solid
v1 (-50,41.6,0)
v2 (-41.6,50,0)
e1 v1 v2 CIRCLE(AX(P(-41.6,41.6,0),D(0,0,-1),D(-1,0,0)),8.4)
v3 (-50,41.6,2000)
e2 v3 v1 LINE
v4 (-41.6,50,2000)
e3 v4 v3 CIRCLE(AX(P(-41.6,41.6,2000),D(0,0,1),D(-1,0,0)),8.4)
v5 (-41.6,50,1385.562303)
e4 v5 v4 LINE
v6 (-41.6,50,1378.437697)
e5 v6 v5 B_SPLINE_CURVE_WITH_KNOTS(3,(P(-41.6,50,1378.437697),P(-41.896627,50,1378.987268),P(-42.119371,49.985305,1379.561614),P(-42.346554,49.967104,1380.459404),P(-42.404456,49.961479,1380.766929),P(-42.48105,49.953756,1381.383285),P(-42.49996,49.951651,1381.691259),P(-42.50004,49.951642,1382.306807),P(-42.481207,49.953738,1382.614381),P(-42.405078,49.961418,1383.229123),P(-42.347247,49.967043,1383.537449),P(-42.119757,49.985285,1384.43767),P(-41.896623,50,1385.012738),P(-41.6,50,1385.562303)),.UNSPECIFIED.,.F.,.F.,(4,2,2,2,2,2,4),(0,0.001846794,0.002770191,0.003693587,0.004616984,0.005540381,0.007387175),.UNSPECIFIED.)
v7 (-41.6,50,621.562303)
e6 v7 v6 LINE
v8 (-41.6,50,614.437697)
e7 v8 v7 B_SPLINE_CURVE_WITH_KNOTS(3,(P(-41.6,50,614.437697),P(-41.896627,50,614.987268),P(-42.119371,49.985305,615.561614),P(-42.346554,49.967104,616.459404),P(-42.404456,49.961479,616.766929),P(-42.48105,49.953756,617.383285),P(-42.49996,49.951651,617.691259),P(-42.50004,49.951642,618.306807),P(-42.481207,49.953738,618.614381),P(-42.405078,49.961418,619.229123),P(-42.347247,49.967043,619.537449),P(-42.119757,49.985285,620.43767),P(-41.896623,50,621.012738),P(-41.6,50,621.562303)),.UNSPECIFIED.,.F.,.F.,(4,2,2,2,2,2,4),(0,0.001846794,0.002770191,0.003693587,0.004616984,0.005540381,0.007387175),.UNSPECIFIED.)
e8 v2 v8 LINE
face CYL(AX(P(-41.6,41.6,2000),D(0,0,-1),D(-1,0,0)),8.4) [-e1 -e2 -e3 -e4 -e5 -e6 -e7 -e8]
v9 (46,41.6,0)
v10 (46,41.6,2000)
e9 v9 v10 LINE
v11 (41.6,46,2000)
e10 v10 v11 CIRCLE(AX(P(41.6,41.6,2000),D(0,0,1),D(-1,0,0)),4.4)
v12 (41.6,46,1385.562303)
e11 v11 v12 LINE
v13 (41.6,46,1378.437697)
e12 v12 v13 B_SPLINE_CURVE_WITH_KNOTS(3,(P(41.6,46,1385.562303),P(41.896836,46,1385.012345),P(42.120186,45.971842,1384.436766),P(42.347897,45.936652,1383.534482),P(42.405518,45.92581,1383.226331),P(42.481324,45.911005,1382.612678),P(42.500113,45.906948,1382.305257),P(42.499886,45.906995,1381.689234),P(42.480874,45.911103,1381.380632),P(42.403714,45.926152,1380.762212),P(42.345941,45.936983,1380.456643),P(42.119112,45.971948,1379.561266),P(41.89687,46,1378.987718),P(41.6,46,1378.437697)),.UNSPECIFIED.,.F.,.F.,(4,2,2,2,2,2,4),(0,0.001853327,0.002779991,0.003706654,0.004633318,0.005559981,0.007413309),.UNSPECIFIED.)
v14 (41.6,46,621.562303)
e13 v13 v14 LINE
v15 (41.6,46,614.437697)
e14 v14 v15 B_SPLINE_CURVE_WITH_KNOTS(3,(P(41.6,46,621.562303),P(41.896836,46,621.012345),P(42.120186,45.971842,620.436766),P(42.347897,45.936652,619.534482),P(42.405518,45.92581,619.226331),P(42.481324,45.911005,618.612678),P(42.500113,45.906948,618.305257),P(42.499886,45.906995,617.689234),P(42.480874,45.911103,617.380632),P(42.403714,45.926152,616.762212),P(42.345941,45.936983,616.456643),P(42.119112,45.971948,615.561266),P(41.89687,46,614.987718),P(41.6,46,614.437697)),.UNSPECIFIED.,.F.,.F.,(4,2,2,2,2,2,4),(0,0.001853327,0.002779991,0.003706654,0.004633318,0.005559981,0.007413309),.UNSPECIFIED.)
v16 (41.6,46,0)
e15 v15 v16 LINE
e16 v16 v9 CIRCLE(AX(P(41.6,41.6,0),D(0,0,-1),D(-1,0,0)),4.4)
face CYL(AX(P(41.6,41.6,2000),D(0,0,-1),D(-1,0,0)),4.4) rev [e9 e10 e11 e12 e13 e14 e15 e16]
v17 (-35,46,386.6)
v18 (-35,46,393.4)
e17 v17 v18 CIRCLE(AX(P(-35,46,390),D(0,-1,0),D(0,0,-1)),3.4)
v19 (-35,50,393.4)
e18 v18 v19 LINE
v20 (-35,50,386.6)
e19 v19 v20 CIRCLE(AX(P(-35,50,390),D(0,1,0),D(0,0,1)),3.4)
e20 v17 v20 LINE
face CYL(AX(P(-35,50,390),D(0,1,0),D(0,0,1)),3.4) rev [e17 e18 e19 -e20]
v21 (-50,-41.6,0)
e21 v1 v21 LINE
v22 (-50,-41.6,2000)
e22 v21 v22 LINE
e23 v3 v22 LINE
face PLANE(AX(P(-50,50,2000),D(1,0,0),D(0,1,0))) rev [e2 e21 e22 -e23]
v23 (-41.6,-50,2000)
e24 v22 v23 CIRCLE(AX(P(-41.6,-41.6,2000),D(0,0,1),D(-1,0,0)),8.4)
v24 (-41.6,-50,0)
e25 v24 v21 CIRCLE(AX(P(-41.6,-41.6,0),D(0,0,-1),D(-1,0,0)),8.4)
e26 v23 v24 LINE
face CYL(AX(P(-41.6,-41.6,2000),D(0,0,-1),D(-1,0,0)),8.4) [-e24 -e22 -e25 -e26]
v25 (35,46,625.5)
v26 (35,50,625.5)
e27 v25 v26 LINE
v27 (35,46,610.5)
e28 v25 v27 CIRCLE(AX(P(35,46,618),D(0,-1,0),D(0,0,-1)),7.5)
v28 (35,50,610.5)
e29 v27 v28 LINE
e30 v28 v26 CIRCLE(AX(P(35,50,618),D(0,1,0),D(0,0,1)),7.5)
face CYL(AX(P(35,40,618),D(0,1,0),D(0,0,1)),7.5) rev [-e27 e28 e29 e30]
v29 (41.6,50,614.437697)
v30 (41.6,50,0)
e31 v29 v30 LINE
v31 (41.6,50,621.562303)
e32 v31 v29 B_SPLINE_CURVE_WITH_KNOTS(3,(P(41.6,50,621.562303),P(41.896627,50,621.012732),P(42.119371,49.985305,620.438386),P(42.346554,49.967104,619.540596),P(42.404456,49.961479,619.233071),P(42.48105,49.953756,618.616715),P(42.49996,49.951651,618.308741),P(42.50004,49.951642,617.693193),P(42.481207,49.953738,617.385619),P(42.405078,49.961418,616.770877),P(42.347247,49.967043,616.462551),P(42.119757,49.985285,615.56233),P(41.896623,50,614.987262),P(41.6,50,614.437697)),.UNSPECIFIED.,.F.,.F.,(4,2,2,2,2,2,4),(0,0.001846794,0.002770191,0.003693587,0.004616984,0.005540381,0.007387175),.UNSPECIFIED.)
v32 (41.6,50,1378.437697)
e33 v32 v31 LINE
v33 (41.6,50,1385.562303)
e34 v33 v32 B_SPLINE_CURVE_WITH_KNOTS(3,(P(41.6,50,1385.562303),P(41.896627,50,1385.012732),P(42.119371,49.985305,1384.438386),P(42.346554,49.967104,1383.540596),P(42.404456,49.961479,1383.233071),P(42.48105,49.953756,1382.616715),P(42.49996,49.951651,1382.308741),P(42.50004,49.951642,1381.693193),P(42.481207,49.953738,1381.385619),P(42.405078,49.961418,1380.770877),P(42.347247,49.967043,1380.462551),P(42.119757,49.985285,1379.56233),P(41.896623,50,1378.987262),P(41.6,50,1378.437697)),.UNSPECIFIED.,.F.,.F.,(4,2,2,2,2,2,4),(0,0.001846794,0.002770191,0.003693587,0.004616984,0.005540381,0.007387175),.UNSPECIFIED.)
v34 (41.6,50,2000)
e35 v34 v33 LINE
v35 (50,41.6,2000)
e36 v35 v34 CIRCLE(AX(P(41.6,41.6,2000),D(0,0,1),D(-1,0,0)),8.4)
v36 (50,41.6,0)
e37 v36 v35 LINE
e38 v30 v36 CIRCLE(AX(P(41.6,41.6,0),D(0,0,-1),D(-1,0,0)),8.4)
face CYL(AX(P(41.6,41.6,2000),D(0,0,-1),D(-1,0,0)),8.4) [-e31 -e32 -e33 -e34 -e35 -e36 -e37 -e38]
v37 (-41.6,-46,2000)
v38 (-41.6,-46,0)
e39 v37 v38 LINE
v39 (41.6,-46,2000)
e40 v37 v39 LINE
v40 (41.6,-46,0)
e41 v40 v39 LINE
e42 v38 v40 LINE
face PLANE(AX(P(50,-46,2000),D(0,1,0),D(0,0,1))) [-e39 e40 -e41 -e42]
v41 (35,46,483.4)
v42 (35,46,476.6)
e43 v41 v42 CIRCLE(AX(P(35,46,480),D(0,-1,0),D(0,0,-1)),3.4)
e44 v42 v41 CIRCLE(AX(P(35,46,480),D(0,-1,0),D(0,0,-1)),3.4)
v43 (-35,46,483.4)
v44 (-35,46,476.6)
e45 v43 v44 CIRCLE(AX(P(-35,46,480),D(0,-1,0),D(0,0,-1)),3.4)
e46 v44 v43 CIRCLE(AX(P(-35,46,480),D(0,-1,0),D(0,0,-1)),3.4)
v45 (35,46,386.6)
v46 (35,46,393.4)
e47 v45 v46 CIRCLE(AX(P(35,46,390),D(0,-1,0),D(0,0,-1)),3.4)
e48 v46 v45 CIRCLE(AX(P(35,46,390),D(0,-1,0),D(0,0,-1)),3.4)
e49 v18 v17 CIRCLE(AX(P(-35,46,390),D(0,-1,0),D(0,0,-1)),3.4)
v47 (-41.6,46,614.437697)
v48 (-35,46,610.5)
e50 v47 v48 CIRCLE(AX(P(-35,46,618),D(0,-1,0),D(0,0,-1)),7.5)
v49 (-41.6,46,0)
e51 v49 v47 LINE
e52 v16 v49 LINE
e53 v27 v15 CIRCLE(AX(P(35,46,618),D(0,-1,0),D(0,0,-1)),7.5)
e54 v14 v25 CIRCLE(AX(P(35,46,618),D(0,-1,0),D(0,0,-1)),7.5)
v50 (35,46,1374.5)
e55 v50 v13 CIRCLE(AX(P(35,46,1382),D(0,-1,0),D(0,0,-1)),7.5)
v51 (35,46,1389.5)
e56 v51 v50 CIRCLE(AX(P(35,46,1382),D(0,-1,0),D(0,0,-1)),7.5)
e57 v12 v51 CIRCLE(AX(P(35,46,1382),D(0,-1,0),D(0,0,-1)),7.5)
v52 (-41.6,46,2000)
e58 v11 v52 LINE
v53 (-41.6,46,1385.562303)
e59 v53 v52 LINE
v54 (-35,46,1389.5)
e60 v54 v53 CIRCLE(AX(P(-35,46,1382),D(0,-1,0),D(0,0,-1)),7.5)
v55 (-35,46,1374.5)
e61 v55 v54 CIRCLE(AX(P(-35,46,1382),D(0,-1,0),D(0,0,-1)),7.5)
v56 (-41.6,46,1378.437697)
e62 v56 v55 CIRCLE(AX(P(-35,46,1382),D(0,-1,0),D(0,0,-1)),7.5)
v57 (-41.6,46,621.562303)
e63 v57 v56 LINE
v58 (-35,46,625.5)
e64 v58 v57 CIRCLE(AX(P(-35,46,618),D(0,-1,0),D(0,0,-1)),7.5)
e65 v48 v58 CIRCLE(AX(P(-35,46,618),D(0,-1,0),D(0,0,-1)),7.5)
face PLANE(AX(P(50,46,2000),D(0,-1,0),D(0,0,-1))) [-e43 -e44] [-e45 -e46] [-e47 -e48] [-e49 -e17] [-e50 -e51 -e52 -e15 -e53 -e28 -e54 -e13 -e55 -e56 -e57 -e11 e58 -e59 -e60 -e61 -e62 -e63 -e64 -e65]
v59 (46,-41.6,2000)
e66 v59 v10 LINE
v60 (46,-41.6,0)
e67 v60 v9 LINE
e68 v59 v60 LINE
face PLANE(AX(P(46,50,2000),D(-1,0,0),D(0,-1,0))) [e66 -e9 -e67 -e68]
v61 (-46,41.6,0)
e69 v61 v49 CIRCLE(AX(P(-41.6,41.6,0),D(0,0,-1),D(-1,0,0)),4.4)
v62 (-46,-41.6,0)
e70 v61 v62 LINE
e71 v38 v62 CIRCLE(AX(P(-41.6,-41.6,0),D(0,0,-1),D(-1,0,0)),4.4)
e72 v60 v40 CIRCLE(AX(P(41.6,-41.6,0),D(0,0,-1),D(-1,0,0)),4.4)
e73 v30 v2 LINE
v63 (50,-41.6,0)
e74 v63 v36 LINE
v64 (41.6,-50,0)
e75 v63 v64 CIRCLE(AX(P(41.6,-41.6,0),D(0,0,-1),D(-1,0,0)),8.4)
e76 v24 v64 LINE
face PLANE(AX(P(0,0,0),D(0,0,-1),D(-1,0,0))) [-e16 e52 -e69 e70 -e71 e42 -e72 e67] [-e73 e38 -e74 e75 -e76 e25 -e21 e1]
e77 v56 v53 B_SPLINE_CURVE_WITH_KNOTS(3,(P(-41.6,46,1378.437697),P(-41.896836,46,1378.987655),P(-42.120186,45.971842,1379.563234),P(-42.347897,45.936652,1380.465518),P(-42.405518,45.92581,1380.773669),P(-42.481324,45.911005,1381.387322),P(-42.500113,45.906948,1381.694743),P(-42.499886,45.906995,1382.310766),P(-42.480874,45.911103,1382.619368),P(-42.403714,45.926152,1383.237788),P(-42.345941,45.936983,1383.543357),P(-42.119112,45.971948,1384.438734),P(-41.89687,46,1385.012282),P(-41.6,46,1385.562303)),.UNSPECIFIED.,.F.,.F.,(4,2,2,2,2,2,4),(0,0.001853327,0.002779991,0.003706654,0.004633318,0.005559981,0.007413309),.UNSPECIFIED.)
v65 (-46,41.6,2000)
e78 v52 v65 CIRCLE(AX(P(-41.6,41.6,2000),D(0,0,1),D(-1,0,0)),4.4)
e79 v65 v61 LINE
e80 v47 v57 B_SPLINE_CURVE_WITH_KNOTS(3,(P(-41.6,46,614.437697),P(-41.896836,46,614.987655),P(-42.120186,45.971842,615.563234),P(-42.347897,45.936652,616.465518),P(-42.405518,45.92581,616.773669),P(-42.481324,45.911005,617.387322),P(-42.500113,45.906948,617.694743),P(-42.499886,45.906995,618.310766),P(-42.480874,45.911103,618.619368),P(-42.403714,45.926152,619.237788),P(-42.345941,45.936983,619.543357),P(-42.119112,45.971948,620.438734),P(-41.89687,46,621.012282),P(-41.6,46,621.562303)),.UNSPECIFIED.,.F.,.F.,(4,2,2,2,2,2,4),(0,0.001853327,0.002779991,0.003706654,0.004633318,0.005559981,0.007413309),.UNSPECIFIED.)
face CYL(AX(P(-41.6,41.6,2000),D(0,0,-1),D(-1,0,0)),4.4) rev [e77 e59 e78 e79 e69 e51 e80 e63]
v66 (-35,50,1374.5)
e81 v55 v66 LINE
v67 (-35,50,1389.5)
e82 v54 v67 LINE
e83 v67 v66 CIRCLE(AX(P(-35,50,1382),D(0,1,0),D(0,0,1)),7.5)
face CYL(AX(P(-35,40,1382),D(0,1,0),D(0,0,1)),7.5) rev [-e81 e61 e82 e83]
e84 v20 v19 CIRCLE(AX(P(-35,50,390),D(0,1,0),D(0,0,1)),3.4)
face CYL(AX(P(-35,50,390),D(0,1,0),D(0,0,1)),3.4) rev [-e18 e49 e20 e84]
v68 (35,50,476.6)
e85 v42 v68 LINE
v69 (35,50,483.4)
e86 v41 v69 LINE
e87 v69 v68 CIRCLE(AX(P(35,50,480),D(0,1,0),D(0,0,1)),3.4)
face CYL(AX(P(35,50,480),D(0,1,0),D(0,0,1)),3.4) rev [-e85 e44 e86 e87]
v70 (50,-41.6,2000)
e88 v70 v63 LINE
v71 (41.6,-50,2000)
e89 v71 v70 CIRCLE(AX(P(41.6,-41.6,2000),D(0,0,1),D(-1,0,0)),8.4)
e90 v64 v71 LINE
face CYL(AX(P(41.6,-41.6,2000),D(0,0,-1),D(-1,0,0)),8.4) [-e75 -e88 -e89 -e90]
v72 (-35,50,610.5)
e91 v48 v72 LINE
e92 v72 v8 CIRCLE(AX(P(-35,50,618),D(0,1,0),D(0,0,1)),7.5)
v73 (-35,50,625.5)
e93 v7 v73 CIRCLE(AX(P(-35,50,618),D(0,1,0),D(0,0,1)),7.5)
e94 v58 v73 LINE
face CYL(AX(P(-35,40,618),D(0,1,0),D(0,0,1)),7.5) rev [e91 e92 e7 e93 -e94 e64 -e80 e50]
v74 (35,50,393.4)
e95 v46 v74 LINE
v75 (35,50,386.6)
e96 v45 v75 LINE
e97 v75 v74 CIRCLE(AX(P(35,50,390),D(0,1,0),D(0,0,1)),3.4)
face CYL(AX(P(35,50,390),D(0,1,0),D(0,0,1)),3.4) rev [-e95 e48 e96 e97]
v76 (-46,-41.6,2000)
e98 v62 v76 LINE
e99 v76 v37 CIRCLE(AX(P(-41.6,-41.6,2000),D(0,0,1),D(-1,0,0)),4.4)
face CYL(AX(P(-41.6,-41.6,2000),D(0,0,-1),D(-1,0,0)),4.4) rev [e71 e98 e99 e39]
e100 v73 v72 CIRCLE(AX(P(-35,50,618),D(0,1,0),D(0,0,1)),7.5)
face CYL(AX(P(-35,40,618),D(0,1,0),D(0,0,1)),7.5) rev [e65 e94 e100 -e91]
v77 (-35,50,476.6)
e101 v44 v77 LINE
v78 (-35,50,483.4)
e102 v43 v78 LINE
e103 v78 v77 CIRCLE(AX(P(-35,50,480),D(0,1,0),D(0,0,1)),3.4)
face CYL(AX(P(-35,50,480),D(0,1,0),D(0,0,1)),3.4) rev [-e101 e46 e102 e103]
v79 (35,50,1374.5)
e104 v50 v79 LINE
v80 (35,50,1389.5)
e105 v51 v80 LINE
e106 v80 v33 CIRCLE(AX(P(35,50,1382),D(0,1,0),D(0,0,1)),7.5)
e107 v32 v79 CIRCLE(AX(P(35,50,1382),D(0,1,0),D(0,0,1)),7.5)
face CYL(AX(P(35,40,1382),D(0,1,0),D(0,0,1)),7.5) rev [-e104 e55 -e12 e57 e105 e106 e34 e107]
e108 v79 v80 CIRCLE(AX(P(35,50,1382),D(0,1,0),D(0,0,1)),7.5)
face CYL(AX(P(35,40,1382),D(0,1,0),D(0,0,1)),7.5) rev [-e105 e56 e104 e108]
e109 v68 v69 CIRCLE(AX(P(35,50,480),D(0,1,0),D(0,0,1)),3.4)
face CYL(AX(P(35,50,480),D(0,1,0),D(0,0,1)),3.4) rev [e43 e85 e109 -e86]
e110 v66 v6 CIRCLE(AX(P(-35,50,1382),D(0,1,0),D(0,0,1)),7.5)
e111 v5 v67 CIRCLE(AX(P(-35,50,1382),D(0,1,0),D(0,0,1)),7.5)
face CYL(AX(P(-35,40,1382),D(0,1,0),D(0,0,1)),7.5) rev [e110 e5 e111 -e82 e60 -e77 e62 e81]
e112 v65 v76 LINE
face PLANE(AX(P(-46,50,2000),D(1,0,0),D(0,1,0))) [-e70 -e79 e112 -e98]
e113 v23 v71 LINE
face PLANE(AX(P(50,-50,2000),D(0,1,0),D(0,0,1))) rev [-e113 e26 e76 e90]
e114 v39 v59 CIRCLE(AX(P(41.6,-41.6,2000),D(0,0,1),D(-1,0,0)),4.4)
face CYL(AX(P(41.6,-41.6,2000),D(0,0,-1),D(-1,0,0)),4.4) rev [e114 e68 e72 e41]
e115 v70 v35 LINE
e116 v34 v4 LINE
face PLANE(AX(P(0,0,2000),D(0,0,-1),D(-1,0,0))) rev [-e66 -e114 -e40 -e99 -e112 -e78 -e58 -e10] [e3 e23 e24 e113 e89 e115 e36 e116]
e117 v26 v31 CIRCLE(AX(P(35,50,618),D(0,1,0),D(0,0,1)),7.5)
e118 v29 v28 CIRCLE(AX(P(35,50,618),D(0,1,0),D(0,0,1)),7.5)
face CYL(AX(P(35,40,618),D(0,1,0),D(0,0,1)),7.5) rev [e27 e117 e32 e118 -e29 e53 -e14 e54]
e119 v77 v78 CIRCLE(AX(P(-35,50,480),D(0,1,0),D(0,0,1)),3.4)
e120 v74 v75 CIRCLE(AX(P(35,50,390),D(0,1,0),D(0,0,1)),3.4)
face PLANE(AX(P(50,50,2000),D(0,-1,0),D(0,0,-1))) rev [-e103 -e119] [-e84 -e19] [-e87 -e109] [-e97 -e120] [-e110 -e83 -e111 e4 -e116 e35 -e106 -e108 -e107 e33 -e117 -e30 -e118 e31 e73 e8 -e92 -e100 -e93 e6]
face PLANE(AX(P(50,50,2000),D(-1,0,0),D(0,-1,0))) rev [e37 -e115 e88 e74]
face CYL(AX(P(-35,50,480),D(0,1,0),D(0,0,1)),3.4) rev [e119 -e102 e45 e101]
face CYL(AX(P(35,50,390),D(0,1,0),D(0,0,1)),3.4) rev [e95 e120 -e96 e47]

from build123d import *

# Parameters (mm, degrees)
SKETCH1_W             = 100
SKETCH1_H             = 100
BOSS_EXTRUDE1_DEPTH   = 2000
FILLET1_R             = 8.4
SHELL1_T              = -4
M8_TAPPED_HOLE1_D     = 6.8
M8_TAPPED_HOLE1_DEPTH = 19.75
M8_TAPPED_HOLE1_TIP   = 2.042926105
SKETCH2_R             = 7.5
SKETCH2_R_2           = 3
CUT_EXTRUDE1_DEPTH    = 10


with BuildPart() as part:
    # Sketch1 → Boss-Extrude1 (new body)
    with BuildSketch(Plane.XY):
        Rectangle(SKETCH1_W, SKETCH1_H)
    extrude(amount=BOSS_EXTRUDE1_DEPTH)

    # Fillet1
    fillet1_edges = [part.edges().sort_by_distance(p)[0] for p in [
        (-50, 50, 1000),
        (50, 50, 1000),
        (50, -50, 1000),
        (-50, -50, 1000),
    ]]
    fillet(fillet1_edges, radius=FILLET1_R)

    # Shell1
    shell1_openings = [part.faces().sort_by_distance(p)[0] for p in [
        (0, 0, 2000),
        (0, 0, 0),
    ]]
    offset(amount=SHELL1_T, openings=shell1_openings, kind=Kind.INTERSECTION)

    # M8 Tapped Hole1
    with Locations(Plane(origin=(0, 50, 0), x_dir=(1, 0, 0), z_dir=(0, 1, 0))):
        with Locations((-35, -390), (35, -390), (35, -480), (-35, -480)):
            Hole(M8_TAPPED_HOLE1_D / 2, depth=M8_TAPPED_HOLE1_DEPTH)
            with Locations((0, 0, -(M8_TAPPED_HOLE1_DEPTH + M8_TAPPED_HOLE1_TIP / 2))):  # 118° drill point
                Cone(0, M8_TAPPED_HOLE1_D / 2, M8_TAPPED_HOLE1_TIP, mode=Mode.SUBTRACT)

    # Sketch2 → Cut-Extrude1 (cut)
    with BuildSketch(Plane(origin=(0, 50, 0), x_dir=(1, 0, 0), z_dir=(0, 1, 0))):
        with Locations(Location((35, -618, 0), (0, 0, 331.642363424))):
            Circle(SKETCH2_R)
        with Locations(Location((-35, -618, 0), (0, 0, 208.357636576))):
            Circle(SKETCH2_R)
        with Locations(Location((35, -1382, 0), (0, 0, 331.642363424))):
            Circle(SKETCH2_R)
        with Locations(Location((-35, -1382, 0), (0, 0, 208.357636576))):
            Circle(SKETCH2_R)
        with Locations((-35, -390)):
            Circle(SKETCH2_R_2)
        with Locations((35, -390)):
            Circle(SKETCH2_R_2)
        with Locations((35, -480)):
            Circle(SKETCH2_R_2)
        with Locations((-35, -480)):
            Circle(SKETCH2_R_2)
    extrude(amount=-CUT_EXTRUDE1_DEPTH, mode=Mode.SUBTRACT)


solid = part.part
